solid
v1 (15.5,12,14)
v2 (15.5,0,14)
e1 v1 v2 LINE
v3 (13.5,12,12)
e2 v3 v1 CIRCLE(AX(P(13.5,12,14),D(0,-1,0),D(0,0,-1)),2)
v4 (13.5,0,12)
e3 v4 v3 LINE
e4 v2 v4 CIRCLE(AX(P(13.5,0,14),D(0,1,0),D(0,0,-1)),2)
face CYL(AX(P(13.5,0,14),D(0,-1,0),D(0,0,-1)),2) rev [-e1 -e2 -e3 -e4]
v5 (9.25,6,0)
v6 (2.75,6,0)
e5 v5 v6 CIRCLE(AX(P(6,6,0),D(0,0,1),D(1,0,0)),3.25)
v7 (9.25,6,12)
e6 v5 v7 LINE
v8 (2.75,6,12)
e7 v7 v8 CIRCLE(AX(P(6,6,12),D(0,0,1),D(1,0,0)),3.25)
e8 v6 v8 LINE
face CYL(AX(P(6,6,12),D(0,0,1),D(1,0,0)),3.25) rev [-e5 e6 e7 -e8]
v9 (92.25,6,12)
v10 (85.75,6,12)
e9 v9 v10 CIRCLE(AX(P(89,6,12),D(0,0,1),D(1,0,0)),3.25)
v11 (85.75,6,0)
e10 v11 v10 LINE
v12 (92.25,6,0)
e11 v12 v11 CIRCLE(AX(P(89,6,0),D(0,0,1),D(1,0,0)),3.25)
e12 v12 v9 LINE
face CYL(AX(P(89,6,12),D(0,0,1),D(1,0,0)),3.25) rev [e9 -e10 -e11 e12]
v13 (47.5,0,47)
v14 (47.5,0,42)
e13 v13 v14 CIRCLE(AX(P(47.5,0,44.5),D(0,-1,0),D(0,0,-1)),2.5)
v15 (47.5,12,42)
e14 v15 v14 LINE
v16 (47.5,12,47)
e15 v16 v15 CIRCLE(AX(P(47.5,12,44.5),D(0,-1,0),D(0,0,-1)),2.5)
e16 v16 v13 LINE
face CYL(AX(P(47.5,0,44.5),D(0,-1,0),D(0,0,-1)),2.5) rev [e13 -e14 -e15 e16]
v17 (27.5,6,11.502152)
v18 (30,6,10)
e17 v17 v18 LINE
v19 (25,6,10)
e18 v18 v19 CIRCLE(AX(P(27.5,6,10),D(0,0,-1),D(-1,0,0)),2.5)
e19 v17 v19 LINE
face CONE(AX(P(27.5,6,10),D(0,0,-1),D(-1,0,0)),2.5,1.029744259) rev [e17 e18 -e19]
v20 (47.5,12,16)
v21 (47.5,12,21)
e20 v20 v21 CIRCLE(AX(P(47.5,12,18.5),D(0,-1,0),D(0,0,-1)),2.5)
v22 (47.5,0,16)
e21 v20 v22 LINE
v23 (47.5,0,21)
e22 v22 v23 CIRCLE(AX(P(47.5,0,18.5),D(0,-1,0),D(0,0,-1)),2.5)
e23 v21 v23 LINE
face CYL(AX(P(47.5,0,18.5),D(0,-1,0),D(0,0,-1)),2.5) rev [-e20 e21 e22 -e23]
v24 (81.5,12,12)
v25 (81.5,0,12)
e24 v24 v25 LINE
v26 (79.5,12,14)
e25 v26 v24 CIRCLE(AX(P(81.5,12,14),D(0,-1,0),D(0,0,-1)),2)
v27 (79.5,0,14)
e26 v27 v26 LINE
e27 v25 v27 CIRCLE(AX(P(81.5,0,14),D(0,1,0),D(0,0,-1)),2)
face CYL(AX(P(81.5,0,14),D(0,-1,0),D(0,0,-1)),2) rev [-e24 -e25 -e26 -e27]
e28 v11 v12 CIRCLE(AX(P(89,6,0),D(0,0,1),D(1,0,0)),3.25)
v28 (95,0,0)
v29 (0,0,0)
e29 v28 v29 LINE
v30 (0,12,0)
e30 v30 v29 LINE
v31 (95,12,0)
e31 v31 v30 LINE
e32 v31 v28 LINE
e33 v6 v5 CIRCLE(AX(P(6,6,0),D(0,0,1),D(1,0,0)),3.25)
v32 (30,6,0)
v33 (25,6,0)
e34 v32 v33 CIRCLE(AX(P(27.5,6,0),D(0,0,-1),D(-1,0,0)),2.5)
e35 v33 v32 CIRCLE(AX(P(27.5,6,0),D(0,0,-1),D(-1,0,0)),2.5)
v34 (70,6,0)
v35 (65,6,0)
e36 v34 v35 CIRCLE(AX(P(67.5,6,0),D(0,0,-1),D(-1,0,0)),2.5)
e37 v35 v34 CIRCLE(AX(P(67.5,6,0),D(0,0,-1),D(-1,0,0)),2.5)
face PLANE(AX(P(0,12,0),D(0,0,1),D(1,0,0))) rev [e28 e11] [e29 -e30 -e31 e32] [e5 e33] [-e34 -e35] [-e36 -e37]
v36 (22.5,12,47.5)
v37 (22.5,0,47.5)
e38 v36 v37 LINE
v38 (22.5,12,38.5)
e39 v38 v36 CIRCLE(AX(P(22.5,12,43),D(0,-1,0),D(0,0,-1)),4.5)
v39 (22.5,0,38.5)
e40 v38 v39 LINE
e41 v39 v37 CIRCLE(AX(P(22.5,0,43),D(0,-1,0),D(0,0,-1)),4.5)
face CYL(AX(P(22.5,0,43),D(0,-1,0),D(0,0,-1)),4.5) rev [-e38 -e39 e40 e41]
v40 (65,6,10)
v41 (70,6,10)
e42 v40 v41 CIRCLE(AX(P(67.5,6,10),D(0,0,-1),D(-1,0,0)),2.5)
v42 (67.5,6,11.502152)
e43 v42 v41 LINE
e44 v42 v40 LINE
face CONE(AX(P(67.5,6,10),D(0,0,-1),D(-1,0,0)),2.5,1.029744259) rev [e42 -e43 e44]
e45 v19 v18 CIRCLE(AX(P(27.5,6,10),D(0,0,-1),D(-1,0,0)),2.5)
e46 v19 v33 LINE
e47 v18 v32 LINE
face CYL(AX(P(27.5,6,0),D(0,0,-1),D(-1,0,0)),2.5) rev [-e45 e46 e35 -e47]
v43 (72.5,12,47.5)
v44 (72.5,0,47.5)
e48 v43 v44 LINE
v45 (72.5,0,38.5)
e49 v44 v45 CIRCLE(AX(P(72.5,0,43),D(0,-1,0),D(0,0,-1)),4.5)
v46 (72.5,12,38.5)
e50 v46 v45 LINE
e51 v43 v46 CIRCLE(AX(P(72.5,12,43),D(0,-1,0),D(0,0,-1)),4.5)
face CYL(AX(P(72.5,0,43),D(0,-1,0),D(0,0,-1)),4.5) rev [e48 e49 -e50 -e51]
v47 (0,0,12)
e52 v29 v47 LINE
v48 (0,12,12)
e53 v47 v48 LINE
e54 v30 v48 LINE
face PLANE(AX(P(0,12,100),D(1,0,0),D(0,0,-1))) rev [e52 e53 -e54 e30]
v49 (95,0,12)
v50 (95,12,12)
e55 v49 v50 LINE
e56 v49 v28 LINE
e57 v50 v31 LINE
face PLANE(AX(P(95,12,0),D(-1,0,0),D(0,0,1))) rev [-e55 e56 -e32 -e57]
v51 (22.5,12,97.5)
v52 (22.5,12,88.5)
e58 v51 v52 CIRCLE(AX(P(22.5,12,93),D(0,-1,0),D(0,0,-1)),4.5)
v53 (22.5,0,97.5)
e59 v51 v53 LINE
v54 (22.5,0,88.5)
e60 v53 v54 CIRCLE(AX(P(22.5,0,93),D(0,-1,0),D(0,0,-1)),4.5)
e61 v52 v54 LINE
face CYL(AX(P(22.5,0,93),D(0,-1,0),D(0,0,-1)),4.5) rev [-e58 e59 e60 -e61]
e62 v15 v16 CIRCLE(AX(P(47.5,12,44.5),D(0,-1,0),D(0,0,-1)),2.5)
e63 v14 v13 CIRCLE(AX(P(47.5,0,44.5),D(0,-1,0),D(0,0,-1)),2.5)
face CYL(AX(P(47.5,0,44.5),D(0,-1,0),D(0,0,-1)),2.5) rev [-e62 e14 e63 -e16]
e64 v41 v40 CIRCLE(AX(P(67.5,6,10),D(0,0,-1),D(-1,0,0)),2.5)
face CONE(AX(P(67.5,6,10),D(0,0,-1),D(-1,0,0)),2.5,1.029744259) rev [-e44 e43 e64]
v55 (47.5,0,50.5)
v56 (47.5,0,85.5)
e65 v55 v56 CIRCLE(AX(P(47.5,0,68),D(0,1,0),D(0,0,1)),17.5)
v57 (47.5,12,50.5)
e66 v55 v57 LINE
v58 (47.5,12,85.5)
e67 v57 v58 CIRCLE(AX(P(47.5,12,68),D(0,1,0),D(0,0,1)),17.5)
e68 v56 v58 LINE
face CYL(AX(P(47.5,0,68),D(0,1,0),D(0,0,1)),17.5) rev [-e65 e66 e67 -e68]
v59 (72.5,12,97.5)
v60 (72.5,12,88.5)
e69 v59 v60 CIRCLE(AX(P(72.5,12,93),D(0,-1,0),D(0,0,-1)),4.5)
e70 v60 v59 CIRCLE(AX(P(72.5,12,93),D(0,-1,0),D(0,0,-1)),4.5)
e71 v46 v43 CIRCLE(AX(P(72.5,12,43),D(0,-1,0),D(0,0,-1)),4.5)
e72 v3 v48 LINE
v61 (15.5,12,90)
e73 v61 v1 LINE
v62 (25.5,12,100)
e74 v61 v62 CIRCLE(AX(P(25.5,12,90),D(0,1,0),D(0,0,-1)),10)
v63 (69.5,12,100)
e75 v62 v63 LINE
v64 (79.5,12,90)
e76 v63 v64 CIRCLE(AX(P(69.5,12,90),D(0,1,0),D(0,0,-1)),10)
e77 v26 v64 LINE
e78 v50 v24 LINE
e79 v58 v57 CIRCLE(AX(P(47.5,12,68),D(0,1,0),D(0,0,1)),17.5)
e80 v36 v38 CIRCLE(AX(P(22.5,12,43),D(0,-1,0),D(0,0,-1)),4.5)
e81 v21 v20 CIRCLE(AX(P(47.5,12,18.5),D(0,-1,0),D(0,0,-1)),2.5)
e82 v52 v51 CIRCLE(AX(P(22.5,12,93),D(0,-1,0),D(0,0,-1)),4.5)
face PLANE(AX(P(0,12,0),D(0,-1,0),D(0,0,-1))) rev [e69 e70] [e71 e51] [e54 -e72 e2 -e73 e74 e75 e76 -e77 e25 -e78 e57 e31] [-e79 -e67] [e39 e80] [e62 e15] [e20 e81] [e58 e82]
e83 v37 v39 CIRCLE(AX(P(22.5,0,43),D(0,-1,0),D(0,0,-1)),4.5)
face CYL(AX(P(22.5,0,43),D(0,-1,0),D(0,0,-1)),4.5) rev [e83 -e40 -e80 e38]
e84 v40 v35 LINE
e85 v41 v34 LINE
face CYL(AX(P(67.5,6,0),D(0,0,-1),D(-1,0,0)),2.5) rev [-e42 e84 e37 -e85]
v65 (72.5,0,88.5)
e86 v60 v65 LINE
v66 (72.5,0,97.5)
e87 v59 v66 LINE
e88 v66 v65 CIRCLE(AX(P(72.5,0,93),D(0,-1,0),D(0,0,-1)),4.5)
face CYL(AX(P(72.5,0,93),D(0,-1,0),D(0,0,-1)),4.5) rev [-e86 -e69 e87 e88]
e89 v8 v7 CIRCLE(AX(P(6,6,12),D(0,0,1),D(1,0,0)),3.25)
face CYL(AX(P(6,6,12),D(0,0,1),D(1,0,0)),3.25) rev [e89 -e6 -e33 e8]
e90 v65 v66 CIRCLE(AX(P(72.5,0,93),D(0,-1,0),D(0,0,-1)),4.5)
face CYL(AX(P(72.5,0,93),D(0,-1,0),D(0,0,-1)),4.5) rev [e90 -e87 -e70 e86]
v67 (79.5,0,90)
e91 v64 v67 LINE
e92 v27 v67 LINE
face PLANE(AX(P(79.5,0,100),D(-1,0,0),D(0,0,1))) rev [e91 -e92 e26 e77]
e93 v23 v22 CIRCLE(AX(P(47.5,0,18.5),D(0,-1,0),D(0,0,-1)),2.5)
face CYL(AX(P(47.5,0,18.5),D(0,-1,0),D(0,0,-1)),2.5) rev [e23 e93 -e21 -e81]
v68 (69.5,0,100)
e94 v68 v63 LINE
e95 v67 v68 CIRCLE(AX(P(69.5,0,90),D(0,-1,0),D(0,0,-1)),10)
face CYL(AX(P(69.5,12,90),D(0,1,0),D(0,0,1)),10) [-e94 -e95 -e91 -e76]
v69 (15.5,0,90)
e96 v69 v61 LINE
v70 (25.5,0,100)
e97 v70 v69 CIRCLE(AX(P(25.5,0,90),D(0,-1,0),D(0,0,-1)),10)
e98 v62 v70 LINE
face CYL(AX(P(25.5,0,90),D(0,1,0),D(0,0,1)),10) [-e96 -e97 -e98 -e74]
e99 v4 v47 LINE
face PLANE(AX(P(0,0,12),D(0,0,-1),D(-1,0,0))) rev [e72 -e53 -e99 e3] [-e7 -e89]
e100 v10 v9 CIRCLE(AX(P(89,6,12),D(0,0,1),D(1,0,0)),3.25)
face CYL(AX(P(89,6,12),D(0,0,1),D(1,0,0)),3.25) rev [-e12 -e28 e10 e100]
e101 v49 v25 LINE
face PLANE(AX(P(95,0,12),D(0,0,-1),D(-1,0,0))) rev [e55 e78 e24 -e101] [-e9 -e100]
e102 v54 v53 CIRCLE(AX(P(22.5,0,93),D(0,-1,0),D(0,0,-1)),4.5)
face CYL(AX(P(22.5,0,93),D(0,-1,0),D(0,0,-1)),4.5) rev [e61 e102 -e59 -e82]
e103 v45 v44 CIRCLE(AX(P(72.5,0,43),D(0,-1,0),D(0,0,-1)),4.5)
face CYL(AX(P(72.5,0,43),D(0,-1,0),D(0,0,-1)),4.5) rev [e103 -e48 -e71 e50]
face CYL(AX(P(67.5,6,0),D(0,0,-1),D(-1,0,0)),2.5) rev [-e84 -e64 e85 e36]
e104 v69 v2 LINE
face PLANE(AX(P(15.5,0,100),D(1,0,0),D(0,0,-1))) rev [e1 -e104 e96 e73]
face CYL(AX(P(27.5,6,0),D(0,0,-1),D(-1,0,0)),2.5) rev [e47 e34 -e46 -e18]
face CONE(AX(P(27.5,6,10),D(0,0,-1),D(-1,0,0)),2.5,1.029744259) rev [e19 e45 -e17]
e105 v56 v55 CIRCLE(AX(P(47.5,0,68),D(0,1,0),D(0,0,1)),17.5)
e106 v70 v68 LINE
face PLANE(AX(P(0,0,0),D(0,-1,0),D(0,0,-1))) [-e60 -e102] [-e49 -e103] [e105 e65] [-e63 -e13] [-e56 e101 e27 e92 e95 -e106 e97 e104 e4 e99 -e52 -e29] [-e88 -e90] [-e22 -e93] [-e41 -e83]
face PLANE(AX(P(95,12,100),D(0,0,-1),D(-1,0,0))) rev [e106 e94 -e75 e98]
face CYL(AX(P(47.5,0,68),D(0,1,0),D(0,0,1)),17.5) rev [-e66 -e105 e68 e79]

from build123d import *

# Parameters (mm, degrees)
SKETCH_1_W                = 95
SKETCH_1_H                = 100
EXTRUDE_1_DEPTH           = 12
SKETCH_9_W                = 15.5
SKETCH_9_H                = 88
CUT_EXTRUDE_4_DEPTH       = 139.452157802
HOLE_WIZARD_6_5_6_5_1_D   = 6.5
SKETCH_12_R               = 17.5
CUT_EXTRUDE_5_DEPTH       = 139.452157802
FILLET_1_R                = 10
HOLE_WIZARD_5_0_5_1_D     = 5
HOLE_WIZARD_5_0_5_1_DEPTH = 10
HOLE_WIZARD_5_0_5_1_TIP   = 1.502151548
FILLET_2_R                = 2
MM_1_D                    = 9
HOLE_WIZARD_M6_1_D        = 5
HOLE_WIZARD_M6_2_D        = 5


with BuildPart() as part:
    # 草图1 → 凸台-拉伸1 (new body)
    with BuildSketch(Plane(origin=(0, 0, 0), x_dir=(1, 0, 0), z_dir=(0, 1, 0))):
        with Locations((47.5, -50)):
            Rectangle(SKETCH_1_W, SKETCH_1_H)
    extrude(amount=EXTRUDE_1_DEPTH)

    # 草图9 → 切除-拉伸4 (cut, through all)
    with BuildSketch(Plane(origin=(0, 12, 0), x_dir=(1, 0, 0), z_dir=(0, 1, 0))):
        with Locations((7.75, -56)):
            Rectangle(SKETCH_9_W, SKETCH_9_H)
        with Locations((87.25, -56)):
            Rectangle(SKETCH_9_W, SKETCH_9_H)
    extrude(amount=-CUT_EXTRUDE_4_DEPTH, mode=Mode.SUBTRACT)

    # Ø6.5 (6.5) 直径孔1 (through all)
    with Locations(Plane.XY.offset(12)):
        with Locations((6, 6), (89, 6)):
            Hole(HOLE_WIZARD_6_5_6_5_1_D / 2)

    # 草图12 → 切除-拉伸5 (cut, through all)
    with BuildSketch(Plane(origin=(0, 12, 0), x_dir=(1, 0, 0), z_dir=(0, 1, 0))):
        with Locations(Location((47.5, -68, 0), (0, 0, 270))):
            Circle(SKETCH_12_R)
    extrude(amount=-CUT_EXTRUDE_5_DEPTH, mode=Mode.SUBTRACT)

    # 圆角1
    fillet_1_edges = [part.edges().sort_by_distance(p)[0] for p in [
        (15.5, 6, 100),
        (79.5, 6, 100),
    ]]
    fillet(fillet_1_edges, radius=FILLET_1_R)

    # Ø5.0 (5) 直径孔1
    with Locations(Plane(origin=(0, 0, 0), x_dir=(-1, 0, 0), z_dir=(0, 0, -1))):
        with Locations((-67.5, 6), (-27.5, 6)):
            Hole(HOLE_WIZARD_5_0_5_1_D / 2, depth=HOLE_WIZARD_5_0_5_1_DEPTH)
            with Locations((0, 0, -(HOLE_WIZARD_5_0_5_1_DEPTH + HOLE_WIZARD_5_0_5_1_TIP / 2))):  # 118° drill point
                Cone(0, HOLE_WIZARD_5_0_5_1_D / 2, HOLE_WIZARD_5_0_5_1_TIP, mode=Mode.SUBTRACT)

    # 圆角2
    fillet_2_edges = [part.edges().sort_by_distance(p)[0] for p in [
        (15.5, 6, 12),
        (79.5, 6, 12),
    ]]
    fillet(fillet_2_edges, radius=FILLET_2_R)

    # 大小mm 暗销孔1 (through all)
    with Locations(Plane(origin=(0, 0, 0), x_dir=(-1, 0, 0), z_dir=(0, -1, 0))):
        with Locations((-72.5, -43), (-72.5, -93), (-22.5, -93), (-22.5, -43)):
            Hole(MM_1_D / 2)

    # M6 螺纹孔1 (through all)
    with Locations(Plane(origin=(0, 0, 0), x_dir=(-1, 0, 0), z_dir=(0, -1, 0))):
        with Locations((-47.5, -44.5)):
            Hole(HOLE_WIZARD_M6_1_D / 2)

    # M6 螺纹孔2 (through all)
    with Locations(Plane(origin=(0, 0, 0), x_dir=(-1, 0, 0), z_dir=(0, -1, 0))):
        with Locations((-47.5, -18.5)):
            Hole(HOLE_WIZARD_M6_2_D / 2)


solid = part.part
